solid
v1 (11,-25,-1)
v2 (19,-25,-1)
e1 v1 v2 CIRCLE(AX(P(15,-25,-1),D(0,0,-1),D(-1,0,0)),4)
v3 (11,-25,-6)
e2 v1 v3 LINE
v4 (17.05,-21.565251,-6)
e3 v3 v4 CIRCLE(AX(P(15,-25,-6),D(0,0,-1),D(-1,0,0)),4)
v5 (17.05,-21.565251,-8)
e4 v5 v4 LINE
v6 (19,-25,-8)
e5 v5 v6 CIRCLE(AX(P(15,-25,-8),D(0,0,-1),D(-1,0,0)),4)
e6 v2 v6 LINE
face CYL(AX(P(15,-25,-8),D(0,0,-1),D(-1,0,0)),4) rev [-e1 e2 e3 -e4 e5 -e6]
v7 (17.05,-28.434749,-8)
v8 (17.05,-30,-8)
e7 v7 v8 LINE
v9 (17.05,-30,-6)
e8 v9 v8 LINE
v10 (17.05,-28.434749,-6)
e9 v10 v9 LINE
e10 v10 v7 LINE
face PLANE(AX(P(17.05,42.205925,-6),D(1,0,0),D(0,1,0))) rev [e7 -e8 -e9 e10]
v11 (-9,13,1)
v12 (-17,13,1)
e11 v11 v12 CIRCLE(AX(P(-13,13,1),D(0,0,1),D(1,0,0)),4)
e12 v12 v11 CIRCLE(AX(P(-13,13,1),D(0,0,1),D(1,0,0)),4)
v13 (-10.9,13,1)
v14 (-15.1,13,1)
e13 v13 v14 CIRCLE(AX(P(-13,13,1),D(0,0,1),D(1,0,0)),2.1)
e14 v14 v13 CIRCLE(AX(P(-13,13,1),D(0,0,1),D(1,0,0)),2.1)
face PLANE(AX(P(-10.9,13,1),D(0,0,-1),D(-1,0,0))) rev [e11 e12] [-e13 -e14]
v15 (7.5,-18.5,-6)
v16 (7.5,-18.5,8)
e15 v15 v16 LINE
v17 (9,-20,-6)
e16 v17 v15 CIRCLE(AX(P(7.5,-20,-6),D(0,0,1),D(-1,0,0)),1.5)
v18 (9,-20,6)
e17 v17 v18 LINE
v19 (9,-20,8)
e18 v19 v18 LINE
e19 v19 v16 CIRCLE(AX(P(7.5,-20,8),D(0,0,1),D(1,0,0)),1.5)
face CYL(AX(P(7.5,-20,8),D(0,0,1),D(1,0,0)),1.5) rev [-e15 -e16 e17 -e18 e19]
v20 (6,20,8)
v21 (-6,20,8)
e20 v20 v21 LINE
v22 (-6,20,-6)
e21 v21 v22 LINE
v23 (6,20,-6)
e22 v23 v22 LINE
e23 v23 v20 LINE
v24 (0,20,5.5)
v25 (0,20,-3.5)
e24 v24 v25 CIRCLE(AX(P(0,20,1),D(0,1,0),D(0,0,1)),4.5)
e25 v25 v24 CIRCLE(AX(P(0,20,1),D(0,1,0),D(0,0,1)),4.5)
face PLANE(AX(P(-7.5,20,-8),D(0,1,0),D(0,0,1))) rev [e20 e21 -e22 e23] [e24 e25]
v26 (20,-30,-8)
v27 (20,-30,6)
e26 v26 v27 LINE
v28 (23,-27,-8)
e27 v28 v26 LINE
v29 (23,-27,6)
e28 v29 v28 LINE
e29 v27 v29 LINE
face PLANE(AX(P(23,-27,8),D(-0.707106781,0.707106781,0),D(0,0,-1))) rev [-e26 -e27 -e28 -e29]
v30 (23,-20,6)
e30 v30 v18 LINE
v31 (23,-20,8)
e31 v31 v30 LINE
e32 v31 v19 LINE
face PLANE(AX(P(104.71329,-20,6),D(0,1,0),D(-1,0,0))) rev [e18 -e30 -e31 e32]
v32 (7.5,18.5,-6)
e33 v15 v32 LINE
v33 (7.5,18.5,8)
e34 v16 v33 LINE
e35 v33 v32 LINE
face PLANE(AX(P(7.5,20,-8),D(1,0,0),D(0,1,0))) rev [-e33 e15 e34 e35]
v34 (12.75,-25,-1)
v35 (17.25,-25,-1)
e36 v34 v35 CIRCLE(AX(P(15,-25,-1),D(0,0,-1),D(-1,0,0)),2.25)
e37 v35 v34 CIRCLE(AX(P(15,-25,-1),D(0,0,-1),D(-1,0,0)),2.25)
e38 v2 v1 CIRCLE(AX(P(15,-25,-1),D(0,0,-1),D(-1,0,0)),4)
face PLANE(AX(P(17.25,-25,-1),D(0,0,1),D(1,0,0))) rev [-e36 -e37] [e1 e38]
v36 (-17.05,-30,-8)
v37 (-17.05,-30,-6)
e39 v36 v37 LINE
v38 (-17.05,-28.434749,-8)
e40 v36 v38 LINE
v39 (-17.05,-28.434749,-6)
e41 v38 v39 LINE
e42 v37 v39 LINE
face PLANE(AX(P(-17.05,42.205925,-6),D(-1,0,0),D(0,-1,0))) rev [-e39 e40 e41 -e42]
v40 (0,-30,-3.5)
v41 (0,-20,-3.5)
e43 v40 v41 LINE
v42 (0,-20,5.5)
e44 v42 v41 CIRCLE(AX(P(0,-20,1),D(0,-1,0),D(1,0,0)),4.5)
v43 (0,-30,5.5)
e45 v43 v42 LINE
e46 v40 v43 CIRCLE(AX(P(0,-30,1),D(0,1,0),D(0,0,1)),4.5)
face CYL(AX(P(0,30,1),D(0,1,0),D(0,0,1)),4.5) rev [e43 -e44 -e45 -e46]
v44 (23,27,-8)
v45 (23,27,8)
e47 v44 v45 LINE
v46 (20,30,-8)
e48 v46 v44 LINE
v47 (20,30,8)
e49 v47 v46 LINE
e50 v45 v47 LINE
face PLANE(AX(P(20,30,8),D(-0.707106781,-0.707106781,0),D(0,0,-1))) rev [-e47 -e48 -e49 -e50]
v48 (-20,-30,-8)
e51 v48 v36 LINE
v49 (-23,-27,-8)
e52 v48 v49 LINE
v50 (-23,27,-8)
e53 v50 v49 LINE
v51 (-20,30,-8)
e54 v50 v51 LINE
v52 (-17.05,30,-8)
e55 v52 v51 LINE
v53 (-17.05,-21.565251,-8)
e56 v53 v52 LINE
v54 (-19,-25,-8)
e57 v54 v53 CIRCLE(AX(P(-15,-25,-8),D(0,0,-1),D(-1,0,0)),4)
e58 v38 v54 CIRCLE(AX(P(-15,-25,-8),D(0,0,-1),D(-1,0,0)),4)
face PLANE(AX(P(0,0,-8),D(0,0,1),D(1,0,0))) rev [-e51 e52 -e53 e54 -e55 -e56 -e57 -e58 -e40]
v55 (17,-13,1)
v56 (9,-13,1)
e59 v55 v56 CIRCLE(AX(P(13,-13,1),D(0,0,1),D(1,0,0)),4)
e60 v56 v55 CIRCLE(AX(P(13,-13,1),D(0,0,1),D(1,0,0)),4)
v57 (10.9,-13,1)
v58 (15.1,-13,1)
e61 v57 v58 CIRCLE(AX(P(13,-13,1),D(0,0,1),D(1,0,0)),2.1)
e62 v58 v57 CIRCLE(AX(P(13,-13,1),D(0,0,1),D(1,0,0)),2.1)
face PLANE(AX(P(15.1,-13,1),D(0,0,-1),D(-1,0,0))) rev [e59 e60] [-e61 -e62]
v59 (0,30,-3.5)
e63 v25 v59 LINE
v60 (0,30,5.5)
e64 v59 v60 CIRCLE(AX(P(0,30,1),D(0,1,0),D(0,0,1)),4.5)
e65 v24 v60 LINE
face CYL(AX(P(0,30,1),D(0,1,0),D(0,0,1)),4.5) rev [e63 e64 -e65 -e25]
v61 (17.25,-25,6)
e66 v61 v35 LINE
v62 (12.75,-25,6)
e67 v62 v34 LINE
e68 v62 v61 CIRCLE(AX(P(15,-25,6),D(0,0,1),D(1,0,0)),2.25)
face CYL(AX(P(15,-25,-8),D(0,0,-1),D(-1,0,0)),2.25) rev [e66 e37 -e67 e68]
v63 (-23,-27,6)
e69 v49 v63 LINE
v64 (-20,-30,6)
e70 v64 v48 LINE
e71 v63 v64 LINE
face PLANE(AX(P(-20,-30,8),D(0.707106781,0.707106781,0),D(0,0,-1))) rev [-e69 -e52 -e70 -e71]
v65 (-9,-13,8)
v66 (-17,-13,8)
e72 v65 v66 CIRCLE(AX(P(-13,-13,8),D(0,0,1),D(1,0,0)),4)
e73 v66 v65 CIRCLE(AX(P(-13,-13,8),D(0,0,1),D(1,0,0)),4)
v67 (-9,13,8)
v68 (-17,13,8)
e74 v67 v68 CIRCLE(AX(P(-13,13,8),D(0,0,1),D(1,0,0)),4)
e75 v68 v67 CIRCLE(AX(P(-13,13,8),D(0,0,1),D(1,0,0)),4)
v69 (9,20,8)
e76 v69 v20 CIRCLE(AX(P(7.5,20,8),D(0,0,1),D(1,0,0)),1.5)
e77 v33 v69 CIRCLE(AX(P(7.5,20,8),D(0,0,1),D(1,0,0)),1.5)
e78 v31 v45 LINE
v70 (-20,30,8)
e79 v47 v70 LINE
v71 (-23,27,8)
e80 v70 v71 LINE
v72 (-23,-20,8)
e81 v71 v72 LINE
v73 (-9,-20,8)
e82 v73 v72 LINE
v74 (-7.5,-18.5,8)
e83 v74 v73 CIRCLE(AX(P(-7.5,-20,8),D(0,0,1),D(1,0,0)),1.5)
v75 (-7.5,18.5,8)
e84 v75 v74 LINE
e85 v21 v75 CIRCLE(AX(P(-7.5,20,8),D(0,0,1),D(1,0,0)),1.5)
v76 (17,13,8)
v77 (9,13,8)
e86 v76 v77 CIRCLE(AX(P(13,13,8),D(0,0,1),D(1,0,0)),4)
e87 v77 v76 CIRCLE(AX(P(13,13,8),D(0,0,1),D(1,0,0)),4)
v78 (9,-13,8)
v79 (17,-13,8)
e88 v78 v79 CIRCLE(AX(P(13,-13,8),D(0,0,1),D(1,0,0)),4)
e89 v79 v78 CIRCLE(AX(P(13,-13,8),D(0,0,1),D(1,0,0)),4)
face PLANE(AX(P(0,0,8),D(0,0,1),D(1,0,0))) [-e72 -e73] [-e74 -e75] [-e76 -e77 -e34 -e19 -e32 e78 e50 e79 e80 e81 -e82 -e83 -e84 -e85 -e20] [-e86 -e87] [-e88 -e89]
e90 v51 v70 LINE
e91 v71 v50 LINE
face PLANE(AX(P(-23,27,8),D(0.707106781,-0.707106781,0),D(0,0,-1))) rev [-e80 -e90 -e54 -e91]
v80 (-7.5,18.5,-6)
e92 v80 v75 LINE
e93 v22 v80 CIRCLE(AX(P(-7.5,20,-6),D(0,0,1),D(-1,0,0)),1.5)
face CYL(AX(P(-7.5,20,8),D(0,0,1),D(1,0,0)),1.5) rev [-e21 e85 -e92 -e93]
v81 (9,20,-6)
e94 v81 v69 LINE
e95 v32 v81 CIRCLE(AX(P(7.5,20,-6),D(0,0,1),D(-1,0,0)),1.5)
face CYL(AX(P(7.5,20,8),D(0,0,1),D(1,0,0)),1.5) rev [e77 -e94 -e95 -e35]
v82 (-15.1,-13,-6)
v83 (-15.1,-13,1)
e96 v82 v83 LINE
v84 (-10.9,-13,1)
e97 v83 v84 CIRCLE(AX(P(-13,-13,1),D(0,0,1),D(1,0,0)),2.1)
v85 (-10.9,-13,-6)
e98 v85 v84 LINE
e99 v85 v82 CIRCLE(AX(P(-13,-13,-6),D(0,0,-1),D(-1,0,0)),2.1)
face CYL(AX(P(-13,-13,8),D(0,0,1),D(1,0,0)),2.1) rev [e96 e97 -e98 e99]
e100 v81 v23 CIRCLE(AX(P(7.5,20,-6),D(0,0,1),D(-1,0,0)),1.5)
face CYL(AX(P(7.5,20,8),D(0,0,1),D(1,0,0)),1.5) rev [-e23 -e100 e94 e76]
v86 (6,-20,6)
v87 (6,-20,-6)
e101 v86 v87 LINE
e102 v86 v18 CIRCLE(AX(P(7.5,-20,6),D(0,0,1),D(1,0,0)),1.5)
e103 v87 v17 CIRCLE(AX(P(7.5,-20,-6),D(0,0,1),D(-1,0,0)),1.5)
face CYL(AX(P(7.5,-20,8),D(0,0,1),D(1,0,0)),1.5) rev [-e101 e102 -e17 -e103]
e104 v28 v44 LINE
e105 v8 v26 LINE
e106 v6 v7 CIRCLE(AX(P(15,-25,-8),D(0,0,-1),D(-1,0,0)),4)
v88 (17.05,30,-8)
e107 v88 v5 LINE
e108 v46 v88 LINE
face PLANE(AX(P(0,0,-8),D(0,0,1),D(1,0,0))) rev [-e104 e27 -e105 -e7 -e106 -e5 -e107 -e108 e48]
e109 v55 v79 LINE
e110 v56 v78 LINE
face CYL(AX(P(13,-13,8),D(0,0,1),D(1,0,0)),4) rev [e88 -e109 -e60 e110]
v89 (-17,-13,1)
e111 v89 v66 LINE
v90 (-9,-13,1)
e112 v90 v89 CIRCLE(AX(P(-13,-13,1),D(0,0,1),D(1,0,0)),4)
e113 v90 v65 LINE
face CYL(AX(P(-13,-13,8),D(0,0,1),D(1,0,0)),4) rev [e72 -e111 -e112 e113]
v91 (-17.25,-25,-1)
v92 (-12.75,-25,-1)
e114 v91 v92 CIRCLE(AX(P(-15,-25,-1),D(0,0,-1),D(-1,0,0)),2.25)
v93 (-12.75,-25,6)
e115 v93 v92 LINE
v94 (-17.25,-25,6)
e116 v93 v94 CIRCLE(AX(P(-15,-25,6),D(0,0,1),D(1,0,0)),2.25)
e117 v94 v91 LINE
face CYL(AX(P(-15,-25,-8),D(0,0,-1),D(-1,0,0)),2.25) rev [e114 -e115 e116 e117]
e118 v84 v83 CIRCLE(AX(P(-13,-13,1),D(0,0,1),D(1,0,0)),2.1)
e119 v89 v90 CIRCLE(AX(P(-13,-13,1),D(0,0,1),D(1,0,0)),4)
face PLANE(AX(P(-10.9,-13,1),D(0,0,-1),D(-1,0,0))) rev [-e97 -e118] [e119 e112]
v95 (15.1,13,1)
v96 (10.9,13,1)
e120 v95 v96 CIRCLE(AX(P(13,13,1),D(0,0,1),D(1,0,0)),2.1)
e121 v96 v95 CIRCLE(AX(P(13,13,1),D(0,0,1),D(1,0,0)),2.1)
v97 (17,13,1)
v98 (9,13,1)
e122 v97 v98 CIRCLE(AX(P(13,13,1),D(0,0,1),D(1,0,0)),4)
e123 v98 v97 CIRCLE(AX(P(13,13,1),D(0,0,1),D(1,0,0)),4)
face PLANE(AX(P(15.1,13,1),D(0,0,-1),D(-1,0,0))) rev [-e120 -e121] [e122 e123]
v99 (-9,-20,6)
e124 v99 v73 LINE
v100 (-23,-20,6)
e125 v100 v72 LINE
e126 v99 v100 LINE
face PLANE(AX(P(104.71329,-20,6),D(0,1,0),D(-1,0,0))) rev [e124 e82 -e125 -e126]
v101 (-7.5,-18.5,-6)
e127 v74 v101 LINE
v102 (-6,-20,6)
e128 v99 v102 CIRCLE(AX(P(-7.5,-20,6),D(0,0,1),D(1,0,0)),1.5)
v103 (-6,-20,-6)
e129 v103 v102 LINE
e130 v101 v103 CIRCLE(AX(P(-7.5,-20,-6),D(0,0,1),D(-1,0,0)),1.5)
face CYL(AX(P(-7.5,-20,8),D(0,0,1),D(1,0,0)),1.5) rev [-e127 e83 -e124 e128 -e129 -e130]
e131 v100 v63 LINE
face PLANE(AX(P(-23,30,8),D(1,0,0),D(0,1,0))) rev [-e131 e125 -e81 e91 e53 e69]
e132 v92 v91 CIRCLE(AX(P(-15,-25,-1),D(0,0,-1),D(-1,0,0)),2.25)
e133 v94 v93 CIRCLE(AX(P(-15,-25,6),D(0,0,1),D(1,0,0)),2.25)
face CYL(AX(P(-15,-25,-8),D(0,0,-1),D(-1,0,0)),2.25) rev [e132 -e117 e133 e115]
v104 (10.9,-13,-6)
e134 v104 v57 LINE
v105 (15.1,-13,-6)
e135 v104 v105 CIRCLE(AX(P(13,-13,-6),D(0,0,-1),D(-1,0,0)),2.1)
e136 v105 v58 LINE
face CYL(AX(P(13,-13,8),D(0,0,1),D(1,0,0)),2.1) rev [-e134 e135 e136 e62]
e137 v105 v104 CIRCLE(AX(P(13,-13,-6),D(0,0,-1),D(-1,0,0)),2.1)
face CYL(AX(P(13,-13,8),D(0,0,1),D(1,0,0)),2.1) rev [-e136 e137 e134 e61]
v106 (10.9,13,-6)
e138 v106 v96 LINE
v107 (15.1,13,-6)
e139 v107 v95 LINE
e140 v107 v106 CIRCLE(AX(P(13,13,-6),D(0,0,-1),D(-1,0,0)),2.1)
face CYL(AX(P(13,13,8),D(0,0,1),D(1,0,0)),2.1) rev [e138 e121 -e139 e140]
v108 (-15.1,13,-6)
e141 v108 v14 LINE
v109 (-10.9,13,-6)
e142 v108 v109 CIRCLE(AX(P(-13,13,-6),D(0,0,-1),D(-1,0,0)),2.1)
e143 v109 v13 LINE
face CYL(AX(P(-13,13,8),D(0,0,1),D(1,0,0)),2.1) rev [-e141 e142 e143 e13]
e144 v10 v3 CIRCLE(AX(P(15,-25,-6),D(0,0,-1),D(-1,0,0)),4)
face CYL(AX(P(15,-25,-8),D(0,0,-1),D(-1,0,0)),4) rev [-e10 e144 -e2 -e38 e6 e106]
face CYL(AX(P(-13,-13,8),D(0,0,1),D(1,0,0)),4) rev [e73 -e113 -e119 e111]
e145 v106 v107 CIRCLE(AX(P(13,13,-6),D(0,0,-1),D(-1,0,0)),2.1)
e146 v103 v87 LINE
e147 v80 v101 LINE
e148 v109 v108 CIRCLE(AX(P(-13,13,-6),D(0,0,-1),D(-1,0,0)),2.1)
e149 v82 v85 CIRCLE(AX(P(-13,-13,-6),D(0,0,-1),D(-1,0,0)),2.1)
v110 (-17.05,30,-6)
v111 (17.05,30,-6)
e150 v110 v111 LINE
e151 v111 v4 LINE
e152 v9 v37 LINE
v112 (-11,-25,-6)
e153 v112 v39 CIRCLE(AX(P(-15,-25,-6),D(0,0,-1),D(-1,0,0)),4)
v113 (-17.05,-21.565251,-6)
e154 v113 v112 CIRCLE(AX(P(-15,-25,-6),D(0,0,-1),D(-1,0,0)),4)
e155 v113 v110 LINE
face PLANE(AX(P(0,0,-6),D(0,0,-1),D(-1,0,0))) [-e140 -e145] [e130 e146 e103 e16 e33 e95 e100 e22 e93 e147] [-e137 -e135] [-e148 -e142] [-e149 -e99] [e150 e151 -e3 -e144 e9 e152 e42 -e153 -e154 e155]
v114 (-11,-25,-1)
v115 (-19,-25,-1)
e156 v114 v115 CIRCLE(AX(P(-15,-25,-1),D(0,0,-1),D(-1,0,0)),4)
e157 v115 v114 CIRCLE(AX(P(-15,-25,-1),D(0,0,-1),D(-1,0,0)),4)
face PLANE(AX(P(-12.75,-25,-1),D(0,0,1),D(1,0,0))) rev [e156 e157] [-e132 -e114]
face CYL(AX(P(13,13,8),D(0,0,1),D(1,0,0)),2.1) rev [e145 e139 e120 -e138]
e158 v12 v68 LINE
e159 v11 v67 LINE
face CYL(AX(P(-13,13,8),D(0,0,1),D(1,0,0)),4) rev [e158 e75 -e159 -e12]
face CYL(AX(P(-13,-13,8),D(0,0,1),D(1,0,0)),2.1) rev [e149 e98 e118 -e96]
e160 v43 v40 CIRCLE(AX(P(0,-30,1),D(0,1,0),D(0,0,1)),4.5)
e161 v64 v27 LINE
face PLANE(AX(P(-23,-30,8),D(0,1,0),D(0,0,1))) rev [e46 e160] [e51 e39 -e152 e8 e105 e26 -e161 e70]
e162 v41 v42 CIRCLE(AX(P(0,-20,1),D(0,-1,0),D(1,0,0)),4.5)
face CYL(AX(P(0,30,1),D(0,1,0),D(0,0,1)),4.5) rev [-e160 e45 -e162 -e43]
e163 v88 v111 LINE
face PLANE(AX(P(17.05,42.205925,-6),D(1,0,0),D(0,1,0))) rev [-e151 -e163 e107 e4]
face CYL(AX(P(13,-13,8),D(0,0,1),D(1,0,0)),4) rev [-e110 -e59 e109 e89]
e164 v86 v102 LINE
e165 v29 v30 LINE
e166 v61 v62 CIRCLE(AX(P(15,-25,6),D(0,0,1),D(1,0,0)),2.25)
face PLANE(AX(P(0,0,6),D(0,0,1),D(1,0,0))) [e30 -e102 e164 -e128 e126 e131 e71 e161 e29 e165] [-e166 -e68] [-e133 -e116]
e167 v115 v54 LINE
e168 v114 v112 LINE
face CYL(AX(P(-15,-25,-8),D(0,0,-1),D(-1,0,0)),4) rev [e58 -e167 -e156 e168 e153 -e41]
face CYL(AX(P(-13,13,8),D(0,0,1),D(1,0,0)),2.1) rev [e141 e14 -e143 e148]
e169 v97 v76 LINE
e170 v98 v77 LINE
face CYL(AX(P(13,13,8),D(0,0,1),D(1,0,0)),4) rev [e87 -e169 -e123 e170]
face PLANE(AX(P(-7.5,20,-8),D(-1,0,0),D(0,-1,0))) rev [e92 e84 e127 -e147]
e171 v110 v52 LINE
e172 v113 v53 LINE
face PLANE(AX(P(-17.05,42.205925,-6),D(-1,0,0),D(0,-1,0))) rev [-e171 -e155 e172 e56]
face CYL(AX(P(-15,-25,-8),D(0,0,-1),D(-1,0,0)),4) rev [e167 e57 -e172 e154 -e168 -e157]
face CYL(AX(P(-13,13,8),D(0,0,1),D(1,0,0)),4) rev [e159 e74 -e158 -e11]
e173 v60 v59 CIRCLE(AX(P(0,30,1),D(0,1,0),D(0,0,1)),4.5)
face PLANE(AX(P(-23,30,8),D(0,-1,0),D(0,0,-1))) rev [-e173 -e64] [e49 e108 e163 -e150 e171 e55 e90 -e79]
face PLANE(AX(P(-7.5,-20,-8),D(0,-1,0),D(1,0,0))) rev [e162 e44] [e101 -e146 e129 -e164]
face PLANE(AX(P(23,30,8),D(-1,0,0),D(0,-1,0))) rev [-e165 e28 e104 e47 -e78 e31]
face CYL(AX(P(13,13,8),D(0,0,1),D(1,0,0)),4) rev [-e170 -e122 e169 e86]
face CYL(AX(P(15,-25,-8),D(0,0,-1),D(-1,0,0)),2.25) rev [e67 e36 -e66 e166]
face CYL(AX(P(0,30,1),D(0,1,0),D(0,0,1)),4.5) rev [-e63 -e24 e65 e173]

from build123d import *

# Parameters (mm, degrees)
SKETCH_1_W                  = 46
SKETCH_1_H                  = 60
EXTRUDE_1_DEPTH             = 8
SKETCH_19_W                 = 142.956519272
SKETCH_19_H                 = 61.410899124
CUT_EXTRUDE_7_DEPTH         = 2
SKETCH_21_W                 = 15
SKETCH_21_H                 = 40
CUT_EXTRUDE_9_DEPTH         = 42.048751504
HOLE_WIZARD_3_0_3_1_D       = 3
HOLE_WIZARD_9_0_9_1_D       = 9
SKETCH_26_W                 = 34.1
SKETCH_26_H                 = 84.411850982
CUT_EXTRUDE_10_DEPTH        = 2
HOLE_WIZARD_3_D             = 4.5
HOLE_WIZARD_3_CBORE_D       = 8
HOLE_WIZARD_3_CBORE_DEPTH   = 7
HOLE_WIZARD_3_2_D           = 4.2
HOLE_WIZARD_3_2_CBORE_D     = 8
HOLE_WIZARD_3_2_CBORE_DEPTH = 7
CHAMFER_2_SIZE              = 3
CHAMFER_1_SIZE              = 3


with BuildPart() as part:
    # 草图1 → 凸台-拉伸1 (new, symmetric)
    with BuildSketch(Plane.XY):
        Rectangle(SKETCH_1_W, SKETCH_1_H)
    extrude(amount=EXTRUDE_1_DEPTH, both=True)

    # 草图19 → 切除-拉伸7 (cut)
    with BuildSketch(Plane.XY.offset(8)):
        with Locations((33.235030531, -50.705449562)):
            Rectangle(SKETCH_19_W, SKETCH_19_H)
    extrude(amount=-CUT_EXTRUDE_7_DEPTH, mode=Mode.SUBTRACT)

    # 草图21 → 切除-拉伸9 (cut, through all)
    with BuildSketch(Plane.XY.offset(8)):
        Rectangle(SKETCH_21_W, SKETCH_21_H)
    extrude(amount=-CUT_EXTRUDE_9_DEPTH, mode=Mode.SUBTRACT)

    # Ø3.0 (3) 直径孔1 (through all)
    with Locations(Plane.XY.offset(8)):
        with Locations((-7.5, 20), (7.5, 20), (-7.5, -20), (7.5, -20)):
            Hole(HOLE_WIZARD_3_0_3_1_D / 2)

    # Ø9.0 (9) 直径孔1 (through all)
    with Locations(Plane(origin=(0, 30, 0), x_dir=(1, 0, 0), z_dir=(0, 1, 0))):
        with Locations((0, -1)):
            Hole(HOLE_WIZARD_9_0_9_1_D / 2)

    # 草图26 → 切除-拉伸10 (cut)
    with BuildSketch(Plane(origin=(0, 0, -8), x_dir=(-1, 0, 0), z_dir=(0, 0, -1))):
        Rectangle(SKETCH_26_W, SKETCH_26_H)
    extrude(amount=-CUT_EXTRUDE_10_DEPTH, mode=Mode.SUBTRACT)

    # Hole Wizard 3 (through all)
    with Locations(Plane(origin=(0, 0, -8), x_dir=(-1, 0, 0), z_dir=(0, 0, -1))):
        with Locations((-15, -25), (15, -25)):
            CounterBoreHole(HOLE_WIZARD_3_D / 2, HOLE_WIZARD_3_CBORE_D / 2, HOLE_WIZARD_3_CBORE_DEPTH)

    # Hole Wizard 3 2 (through all)
    with Locations(Plane.XY.offset(8)):
        with Locations((-13, 13), (13, 13), (-13, -13), (13, -13)):
            CounterBoreHole(HOLE_WIZARD_3_2_D / 2, HOLE_WIZARD_3_2_CBORE_D / 2, HOLE_WIZARD_3_2_CBORE_DEPTH)

    # 倒角2
    chamfer_2_edges = [part.edges().sort_by_distance(p)[0] for p in [
        (-23, 30, 0),
        (23, 30, 0),
    ]]
    chamfer(chamfer_2_edges, length=CHAMFER_2_SIZE)

    # 倒角1
    chamfer_1_edges = [part.edges().sort_by_distance(p)[0] for p in [
        (23, -30, -1),
        (-23, -30, -1),
    ]]
    chamfer(chamfer_1_edges, length=CHAMFER_1_SIZE)


solid = part.part
